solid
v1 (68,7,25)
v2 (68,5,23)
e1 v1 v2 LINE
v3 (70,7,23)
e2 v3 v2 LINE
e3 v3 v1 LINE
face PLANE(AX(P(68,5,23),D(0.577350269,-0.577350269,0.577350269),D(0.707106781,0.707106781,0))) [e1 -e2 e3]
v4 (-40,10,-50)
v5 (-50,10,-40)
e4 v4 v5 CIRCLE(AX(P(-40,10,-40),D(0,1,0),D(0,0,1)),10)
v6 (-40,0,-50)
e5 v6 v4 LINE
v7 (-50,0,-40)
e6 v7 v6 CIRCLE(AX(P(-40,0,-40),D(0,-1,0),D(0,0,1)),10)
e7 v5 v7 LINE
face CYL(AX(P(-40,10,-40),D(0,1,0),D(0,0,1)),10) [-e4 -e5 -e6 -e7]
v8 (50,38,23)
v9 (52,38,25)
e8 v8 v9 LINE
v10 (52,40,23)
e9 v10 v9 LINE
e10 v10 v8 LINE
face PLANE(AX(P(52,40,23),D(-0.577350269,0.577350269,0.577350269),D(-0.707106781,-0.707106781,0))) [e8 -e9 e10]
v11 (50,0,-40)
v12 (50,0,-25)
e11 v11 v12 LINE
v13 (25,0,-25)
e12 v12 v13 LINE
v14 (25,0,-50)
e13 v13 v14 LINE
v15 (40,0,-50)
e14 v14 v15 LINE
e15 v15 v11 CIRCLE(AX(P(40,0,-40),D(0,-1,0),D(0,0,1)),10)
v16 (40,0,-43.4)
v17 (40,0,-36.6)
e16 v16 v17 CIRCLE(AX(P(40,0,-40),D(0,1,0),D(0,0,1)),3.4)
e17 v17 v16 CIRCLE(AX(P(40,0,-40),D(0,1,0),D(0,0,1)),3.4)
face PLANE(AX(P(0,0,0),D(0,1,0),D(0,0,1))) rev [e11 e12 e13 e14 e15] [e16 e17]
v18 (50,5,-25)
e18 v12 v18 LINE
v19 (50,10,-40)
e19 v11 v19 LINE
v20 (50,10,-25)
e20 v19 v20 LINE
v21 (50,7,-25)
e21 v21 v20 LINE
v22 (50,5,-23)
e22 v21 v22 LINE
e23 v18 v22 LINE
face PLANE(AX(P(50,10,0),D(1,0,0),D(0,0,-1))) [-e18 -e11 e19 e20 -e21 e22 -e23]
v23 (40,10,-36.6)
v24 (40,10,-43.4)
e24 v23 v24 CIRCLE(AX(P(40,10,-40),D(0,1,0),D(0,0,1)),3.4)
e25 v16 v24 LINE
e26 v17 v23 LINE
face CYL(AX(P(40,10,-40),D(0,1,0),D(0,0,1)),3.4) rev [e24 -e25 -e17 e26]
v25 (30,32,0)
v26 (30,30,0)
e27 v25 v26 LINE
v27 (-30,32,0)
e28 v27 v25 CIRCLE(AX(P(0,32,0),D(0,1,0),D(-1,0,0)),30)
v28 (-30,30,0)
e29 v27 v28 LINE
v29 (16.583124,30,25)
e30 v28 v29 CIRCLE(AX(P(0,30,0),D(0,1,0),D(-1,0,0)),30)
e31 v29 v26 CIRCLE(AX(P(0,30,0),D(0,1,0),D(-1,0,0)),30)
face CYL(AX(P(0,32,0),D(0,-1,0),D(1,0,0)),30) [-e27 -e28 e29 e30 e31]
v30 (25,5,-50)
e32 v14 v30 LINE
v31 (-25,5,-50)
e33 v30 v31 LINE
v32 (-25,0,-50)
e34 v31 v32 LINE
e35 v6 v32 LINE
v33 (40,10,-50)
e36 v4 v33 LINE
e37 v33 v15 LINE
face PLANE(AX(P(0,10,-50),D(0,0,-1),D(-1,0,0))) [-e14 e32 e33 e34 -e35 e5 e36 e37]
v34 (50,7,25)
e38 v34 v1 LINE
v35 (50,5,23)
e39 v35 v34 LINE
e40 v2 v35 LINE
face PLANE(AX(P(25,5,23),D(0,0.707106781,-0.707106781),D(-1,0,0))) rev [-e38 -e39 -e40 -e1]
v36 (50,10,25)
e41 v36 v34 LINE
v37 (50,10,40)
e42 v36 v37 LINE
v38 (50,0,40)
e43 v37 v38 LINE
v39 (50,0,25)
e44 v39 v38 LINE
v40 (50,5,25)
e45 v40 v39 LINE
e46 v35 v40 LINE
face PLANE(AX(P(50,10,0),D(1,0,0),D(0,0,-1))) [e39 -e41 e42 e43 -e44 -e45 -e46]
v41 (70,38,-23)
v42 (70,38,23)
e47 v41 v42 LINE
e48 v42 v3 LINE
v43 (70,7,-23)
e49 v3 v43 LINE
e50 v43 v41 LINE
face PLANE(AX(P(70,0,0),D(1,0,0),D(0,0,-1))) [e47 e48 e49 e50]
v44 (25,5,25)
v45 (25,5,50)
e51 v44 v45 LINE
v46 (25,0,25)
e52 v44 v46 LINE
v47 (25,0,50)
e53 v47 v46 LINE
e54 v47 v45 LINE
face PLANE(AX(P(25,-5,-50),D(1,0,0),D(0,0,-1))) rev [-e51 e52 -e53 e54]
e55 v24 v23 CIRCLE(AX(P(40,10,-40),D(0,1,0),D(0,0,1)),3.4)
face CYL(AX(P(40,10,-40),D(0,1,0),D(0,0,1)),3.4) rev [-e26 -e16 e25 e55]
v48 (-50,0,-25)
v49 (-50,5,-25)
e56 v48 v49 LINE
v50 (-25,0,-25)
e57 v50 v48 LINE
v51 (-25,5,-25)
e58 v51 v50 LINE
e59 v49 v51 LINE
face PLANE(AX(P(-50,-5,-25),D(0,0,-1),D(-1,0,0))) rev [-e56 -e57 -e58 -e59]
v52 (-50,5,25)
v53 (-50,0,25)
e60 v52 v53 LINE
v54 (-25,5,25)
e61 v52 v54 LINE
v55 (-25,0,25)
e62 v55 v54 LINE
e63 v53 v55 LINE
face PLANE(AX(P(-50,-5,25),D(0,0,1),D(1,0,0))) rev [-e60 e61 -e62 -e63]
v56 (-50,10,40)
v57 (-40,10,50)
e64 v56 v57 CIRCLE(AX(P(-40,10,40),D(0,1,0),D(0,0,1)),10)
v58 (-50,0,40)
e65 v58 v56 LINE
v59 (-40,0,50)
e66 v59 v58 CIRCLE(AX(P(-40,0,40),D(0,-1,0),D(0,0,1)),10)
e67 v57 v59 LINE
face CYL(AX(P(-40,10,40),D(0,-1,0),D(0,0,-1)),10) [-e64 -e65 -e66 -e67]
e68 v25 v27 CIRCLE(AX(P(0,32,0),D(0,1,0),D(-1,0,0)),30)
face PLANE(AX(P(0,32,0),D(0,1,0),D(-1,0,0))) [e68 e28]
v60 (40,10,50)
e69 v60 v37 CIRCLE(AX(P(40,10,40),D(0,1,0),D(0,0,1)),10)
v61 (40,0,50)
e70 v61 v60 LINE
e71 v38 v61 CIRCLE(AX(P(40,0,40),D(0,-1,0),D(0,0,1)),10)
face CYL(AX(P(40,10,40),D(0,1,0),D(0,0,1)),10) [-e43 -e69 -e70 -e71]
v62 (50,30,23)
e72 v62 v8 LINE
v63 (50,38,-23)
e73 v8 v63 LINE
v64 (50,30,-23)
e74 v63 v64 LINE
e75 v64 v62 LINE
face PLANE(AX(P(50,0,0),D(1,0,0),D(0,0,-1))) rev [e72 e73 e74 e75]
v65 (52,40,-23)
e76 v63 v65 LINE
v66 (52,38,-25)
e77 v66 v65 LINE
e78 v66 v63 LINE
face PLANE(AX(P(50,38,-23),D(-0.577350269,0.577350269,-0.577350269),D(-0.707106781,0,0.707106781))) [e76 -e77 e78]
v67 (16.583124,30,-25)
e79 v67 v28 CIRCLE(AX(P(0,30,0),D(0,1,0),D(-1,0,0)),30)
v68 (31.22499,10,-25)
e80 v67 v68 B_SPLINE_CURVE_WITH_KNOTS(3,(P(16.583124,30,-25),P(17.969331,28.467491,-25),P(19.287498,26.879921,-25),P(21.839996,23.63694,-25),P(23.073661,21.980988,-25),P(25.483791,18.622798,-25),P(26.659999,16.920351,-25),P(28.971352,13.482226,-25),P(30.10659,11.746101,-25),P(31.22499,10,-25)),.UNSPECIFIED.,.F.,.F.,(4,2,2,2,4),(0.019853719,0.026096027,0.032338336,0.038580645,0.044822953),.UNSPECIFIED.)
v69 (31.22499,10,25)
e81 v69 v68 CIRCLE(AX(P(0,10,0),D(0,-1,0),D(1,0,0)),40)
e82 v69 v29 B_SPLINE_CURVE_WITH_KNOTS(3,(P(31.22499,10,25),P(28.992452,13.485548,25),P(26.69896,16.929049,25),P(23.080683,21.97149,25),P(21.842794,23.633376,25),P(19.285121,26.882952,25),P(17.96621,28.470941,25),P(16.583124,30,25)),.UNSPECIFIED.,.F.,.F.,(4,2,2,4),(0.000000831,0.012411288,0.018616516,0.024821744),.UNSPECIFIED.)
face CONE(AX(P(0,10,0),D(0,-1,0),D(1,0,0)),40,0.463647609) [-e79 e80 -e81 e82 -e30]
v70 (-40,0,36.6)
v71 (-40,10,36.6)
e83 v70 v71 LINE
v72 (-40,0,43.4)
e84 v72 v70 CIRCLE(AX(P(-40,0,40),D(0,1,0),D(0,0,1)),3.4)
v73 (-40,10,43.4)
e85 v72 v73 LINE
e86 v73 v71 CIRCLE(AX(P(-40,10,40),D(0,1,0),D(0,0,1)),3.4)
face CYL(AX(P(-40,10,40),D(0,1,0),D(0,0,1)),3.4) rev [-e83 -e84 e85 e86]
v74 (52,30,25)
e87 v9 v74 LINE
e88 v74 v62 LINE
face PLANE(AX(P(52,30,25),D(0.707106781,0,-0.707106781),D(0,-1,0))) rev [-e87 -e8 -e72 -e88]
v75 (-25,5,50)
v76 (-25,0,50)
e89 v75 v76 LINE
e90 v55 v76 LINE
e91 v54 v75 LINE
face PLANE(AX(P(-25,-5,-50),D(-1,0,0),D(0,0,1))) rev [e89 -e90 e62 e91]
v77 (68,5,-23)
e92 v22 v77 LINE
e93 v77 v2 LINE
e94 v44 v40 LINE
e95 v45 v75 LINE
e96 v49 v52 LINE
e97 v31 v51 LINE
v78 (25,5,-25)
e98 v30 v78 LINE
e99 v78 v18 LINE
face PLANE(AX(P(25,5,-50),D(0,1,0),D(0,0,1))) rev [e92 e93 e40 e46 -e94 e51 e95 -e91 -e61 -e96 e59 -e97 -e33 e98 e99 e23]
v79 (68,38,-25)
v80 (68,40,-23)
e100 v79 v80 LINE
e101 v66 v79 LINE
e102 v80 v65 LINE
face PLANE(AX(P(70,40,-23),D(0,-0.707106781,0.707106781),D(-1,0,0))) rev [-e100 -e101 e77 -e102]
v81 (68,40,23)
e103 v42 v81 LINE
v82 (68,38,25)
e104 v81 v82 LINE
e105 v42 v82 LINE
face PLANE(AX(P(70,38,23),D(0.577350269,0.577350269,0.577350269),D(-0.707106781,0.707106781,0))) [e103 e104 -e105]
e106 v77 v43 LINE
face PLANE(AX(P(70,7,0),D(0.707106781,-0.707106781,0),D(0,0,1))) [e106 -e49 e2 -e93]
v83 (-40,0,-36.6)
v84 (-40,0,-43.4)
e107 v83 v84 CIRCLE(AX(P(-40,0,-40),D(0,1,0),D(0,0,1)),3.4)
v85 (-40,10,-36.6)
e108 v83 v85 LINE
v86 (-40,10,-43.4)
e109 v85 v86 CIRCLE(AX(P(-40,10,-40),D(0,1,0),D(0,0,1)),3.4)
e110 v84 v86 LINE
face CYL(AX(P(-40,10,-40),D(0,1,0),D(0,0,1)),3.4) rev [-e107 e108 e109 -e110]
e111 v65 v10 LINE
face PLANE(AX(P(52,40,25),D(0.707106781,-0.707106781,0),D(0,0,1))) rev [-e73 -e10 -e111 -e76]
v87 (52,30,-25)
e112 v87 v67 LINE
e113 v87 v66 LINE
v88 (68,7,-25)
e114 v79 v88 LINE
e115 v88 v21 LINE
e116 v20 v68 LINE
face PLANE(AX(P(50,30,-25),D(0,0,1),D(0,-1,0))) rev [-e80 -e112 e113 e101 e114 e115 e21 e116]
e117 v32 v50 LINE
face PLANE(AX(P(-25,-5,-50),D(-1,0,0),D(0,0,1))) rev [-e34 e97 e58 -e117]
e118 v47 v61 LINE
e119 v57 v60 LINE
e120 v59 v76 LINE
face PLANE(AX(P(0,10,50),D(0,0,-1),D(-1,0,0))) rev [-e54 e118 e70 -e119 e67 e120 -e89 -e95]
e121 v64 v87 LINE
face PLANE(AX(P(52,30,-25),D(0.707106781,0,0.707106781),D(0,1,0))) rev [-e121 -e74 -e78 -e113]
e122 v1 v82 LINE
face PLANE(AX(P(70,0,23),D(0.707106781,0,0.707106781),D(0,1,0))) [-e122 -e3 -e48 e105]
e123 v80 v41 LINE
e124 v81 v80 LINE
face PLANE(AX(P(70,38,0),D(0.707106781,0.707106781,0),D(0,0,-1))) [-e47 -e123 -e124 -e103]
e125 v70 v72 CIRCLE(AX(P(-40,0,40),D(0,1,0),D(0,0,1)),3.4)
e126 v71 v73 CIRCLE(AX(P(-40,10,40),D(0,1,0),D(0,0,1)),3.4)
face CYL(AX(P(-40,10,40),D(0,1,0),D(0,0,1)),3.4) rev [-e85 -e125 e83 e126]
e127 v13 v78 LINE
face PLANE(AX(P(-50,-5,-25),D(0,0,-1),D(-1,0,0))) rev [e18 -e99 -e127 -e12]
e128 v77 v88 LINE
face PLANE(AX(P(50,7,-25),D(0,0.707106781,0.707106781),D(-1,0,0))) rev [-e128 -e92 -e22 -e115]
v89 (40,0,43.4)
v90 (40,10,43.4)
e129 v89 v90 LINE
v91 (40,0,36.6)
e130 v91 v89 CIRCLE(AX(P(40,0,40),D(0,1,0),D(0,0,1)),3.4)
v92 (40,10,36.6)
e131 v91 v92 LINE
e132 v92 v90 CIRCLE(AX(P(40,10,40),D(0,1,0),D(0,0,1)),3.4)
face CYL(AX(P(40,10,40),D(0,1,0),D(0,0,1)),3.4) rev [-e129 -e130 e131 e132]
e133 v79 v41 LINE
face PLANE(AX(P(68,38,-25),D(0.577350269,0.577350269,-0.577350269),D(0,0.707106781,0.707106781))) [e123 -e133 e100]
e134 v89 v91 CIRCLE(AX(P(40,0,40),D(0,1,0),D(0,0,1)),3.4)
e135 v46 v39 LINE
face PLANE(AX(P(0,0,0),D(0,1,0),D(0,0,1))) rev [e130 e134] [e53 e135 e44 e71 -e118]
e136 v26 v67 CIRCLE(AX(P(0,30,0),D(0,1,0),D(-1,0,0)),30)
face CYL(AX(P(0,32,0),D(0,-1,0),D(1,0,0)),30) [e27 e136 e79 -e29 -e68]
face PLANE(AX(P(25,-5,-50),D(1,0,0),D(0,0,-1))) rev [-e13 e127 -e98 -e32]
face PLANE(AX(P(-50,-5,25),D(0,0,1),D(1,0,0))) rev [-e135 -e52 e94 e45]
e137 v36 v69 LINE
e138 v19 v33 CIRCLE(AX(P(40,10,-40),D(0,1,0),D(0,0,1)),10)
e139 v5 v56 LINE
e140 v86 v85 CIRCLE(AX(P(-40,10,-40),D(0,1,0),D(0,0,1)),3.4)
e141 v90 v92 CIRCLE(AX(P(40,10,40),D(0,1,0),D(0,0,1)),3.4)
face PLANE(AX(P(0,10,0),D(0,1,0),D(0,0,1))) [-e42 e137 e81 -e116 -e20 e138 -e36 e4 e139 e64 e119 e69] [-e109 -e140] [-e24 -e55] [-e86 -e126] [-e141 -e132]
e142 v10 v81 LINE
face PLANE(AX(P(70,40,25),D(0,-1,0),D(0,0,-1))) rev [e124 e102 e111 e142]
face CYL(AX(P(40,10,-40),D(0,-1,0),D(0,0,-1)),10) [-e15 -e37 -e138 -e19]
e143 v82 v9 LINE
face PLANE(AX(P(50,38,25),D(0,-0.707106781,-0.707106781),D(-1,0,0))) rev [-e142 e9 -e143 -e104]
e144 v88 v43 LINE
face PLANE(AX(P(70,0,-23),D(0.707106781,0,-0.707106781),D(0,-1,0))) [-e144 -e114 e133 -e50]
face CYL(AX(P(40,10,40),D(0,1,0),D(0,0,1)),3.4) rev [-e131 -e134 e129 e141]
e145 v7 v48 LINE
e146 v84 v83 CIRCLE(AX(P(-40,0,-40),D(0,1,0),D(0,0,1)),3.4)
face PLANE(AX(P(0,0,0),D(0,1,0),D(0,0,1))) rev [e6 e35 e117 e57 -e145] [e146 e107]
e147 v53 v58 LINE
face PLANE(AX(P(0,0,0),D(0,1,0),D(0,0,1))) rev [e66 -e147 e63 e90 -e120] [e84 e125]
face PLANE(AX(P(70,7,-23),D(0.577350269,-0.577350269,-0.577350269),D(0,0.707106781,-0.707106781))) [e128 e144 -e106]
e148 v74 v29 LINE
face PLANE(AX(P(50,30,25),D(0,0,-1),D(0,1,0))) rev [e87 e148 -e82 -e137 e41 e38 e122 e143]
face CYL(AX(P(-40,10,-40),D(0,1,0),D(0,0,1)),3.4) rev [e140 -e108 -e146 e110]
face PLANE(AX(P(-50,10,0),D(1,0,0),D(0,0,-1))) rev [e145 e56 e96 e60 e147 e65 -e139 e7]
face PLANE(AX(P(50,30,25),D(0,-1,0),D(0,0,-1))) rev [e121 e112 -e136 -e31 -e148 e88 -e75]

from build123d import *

# Parameters (mm, degrees)
SKETCH1_W             = 100
SKETCH1_H             = 100
BOSS_EXTRUDE1_DEPTH   = 10
SKETCH2_W             = 50
SKETCH2_H             = 10
CUT_EXTRUDE1_DEPTH    = 113.249721603
SKETCH3_W             = 50
SKETCH3_H             = 10
CUT_EXTRUDE2_DEPTH    = 113.249721603
FILLET1_R             = 10
SKETCH5_R             = 30
BOSS_EXTRUDE2_DEPTH   = 2
SKETCH6_W             = 50
SKETCH6_H             = 20
BOSS_EXTRUDE3_DEPTH   = 50
SKETCH7_W             = 50
SKETCH7_H             = 35
BOSS_EXTRUDE6_DEPTH   = 20
CHAMFER1_SIZE         = 2
M8_TAPPED_HOLE1_D     = 6.8
M8_TAPPED_HOLE1_DEPTH = 20.207073895
M8_TAPPED_HOLE1_TIP   = 2.042926105


with BuildPart() as part:
    # Sketch1 → Boss-Extrude1 (new body)
    with BuildSketch(Plane(origin=(0, 0, 0), x_dir=(1, 0, 0), z_dir=(0, 1, 0))):
        Rectangle(SKETCH1_W, SKETCH1_H)
    extrude(amount=BOSS_EXTRUDE1_DEPTH)

    # Sketch2 → Cut-Extrude1 (cut, through all)
    with BuildSketch(Plane.XY.offset(50)):
        Rectangle(SKETCH2_W, SKETCH2_H)
    extrude(amount=-CUT_EXTRUDE1_DEPTH, mode=Mode.SUBTRACT)

    # Sketch3 → Cut-Extrude2 (cut, through all)
    with BuildSketch(Plane(origin=(50, 0, 0), x_dir=(0, 0, -1), z_dir=(1, 0, 0))):
        Rectangle(SKETCH3_W, SKETCH3_H)
    extrude(amount=-CUT_EXTRUDE2_DEPTH, mode=Mode.SUBTRACT)

    # Fillet1
    fillet1_edges = [part.edges().sort_by_distance(p)[0] for p in [
        (50, 5, 50),
        (-50, 5, 50),
        (-50, 5, -50),
        (50, 5, -50),
    ]]
    fillet(fillet1_edges, radius=FILLET1_R)

    # Sketch4 → Revolve1 (revolve)
    with BuildSketch(Plane.XY):
        Polygon((0, 10), (0, 30), (30, 30), (40, 10), align=None)
    revolve(axis=Axis((0, 10, 0), (0, 1, 0)))

    # Sketch5 → Boss-Extrude2 (add)
    with BuildSketch(Plane(origin=(0, 30, 0), x_dir=(1, 0, 0), z_dir=(0, 1, 0))):
        with Locations(Location((0, 0, 0), (0, 0, 180))):
            Circle(SKETCH5_R)
    extrude(amount=BOSS_EXTRUDE2_DEPTH)

    # Sketch6 → Boss-Extrude3 (add)
    with BuildSketch(Plane(origin=(0, 0, 0), x_dir=(0, 0, -1), z_dir=(1, 0, 0))):
        with Locations((0, 20)):
            Rectangle(SKETCH6_W, SKETCH6_H)
    extrude(amount=BOSS_EXTRUDE3_DEPTH)

    # Sketch7 → Boss-Extrude6 (add)
    with BuildSketch(Plane(origin=(50, 0, 0), x_dir=(0, 0, -1), z_dir=(1, 0, 0))):
        with Locations((0, 22.5)):
            Rectangle(SKETCH7_W, SKETCH7_H)
    extrude(amount=BOSS_EXTRUDE6_DEPTH)

    # Chamfer1
    chamfer1_edges = [part.edges().sort_by_distance(p)[0] for p in [
        (70, 5, 0),
        (50, 40, 0),
        (60, 5, -25),
        (50, 35, -25),
        (60, 40, -25),
        (70, 22.5, -25),
        (70, 40, 0),
        (60, 5, 25),
        (70, 22.5, 25),
        (60, 40, 25),
        (50, 35, 25),
    ]]
    chamfer(chamfer1_edges, length=CHAMFER1_SIZE)

    # M8 Tapped Hole1
    with Locations(Plane(origin=(0, 10, 0), x_dir=(1, 0, 0), z_dir=(0, 1, 0))):
        with Locations((40, 40), (40, -40), (-40, -40), (-40, 40)):
            Hole(M8_TAPPED_HOLE1_D / 2, depth=M8_TAPPED_HOLE1_DEPTH)
            with Locations((0, 0, -(M8_TAPPED_HOLE1_DEPTH + M8_TAPPED_HOLE1_TIP / 2))):  # 118° drill point
                Cone(0, M8_TAPPED_HOLE1_D / 2, M8_TAPPED_HOLE1_TIP, mode=Mode.SUBTRACT)


solid = part.part
